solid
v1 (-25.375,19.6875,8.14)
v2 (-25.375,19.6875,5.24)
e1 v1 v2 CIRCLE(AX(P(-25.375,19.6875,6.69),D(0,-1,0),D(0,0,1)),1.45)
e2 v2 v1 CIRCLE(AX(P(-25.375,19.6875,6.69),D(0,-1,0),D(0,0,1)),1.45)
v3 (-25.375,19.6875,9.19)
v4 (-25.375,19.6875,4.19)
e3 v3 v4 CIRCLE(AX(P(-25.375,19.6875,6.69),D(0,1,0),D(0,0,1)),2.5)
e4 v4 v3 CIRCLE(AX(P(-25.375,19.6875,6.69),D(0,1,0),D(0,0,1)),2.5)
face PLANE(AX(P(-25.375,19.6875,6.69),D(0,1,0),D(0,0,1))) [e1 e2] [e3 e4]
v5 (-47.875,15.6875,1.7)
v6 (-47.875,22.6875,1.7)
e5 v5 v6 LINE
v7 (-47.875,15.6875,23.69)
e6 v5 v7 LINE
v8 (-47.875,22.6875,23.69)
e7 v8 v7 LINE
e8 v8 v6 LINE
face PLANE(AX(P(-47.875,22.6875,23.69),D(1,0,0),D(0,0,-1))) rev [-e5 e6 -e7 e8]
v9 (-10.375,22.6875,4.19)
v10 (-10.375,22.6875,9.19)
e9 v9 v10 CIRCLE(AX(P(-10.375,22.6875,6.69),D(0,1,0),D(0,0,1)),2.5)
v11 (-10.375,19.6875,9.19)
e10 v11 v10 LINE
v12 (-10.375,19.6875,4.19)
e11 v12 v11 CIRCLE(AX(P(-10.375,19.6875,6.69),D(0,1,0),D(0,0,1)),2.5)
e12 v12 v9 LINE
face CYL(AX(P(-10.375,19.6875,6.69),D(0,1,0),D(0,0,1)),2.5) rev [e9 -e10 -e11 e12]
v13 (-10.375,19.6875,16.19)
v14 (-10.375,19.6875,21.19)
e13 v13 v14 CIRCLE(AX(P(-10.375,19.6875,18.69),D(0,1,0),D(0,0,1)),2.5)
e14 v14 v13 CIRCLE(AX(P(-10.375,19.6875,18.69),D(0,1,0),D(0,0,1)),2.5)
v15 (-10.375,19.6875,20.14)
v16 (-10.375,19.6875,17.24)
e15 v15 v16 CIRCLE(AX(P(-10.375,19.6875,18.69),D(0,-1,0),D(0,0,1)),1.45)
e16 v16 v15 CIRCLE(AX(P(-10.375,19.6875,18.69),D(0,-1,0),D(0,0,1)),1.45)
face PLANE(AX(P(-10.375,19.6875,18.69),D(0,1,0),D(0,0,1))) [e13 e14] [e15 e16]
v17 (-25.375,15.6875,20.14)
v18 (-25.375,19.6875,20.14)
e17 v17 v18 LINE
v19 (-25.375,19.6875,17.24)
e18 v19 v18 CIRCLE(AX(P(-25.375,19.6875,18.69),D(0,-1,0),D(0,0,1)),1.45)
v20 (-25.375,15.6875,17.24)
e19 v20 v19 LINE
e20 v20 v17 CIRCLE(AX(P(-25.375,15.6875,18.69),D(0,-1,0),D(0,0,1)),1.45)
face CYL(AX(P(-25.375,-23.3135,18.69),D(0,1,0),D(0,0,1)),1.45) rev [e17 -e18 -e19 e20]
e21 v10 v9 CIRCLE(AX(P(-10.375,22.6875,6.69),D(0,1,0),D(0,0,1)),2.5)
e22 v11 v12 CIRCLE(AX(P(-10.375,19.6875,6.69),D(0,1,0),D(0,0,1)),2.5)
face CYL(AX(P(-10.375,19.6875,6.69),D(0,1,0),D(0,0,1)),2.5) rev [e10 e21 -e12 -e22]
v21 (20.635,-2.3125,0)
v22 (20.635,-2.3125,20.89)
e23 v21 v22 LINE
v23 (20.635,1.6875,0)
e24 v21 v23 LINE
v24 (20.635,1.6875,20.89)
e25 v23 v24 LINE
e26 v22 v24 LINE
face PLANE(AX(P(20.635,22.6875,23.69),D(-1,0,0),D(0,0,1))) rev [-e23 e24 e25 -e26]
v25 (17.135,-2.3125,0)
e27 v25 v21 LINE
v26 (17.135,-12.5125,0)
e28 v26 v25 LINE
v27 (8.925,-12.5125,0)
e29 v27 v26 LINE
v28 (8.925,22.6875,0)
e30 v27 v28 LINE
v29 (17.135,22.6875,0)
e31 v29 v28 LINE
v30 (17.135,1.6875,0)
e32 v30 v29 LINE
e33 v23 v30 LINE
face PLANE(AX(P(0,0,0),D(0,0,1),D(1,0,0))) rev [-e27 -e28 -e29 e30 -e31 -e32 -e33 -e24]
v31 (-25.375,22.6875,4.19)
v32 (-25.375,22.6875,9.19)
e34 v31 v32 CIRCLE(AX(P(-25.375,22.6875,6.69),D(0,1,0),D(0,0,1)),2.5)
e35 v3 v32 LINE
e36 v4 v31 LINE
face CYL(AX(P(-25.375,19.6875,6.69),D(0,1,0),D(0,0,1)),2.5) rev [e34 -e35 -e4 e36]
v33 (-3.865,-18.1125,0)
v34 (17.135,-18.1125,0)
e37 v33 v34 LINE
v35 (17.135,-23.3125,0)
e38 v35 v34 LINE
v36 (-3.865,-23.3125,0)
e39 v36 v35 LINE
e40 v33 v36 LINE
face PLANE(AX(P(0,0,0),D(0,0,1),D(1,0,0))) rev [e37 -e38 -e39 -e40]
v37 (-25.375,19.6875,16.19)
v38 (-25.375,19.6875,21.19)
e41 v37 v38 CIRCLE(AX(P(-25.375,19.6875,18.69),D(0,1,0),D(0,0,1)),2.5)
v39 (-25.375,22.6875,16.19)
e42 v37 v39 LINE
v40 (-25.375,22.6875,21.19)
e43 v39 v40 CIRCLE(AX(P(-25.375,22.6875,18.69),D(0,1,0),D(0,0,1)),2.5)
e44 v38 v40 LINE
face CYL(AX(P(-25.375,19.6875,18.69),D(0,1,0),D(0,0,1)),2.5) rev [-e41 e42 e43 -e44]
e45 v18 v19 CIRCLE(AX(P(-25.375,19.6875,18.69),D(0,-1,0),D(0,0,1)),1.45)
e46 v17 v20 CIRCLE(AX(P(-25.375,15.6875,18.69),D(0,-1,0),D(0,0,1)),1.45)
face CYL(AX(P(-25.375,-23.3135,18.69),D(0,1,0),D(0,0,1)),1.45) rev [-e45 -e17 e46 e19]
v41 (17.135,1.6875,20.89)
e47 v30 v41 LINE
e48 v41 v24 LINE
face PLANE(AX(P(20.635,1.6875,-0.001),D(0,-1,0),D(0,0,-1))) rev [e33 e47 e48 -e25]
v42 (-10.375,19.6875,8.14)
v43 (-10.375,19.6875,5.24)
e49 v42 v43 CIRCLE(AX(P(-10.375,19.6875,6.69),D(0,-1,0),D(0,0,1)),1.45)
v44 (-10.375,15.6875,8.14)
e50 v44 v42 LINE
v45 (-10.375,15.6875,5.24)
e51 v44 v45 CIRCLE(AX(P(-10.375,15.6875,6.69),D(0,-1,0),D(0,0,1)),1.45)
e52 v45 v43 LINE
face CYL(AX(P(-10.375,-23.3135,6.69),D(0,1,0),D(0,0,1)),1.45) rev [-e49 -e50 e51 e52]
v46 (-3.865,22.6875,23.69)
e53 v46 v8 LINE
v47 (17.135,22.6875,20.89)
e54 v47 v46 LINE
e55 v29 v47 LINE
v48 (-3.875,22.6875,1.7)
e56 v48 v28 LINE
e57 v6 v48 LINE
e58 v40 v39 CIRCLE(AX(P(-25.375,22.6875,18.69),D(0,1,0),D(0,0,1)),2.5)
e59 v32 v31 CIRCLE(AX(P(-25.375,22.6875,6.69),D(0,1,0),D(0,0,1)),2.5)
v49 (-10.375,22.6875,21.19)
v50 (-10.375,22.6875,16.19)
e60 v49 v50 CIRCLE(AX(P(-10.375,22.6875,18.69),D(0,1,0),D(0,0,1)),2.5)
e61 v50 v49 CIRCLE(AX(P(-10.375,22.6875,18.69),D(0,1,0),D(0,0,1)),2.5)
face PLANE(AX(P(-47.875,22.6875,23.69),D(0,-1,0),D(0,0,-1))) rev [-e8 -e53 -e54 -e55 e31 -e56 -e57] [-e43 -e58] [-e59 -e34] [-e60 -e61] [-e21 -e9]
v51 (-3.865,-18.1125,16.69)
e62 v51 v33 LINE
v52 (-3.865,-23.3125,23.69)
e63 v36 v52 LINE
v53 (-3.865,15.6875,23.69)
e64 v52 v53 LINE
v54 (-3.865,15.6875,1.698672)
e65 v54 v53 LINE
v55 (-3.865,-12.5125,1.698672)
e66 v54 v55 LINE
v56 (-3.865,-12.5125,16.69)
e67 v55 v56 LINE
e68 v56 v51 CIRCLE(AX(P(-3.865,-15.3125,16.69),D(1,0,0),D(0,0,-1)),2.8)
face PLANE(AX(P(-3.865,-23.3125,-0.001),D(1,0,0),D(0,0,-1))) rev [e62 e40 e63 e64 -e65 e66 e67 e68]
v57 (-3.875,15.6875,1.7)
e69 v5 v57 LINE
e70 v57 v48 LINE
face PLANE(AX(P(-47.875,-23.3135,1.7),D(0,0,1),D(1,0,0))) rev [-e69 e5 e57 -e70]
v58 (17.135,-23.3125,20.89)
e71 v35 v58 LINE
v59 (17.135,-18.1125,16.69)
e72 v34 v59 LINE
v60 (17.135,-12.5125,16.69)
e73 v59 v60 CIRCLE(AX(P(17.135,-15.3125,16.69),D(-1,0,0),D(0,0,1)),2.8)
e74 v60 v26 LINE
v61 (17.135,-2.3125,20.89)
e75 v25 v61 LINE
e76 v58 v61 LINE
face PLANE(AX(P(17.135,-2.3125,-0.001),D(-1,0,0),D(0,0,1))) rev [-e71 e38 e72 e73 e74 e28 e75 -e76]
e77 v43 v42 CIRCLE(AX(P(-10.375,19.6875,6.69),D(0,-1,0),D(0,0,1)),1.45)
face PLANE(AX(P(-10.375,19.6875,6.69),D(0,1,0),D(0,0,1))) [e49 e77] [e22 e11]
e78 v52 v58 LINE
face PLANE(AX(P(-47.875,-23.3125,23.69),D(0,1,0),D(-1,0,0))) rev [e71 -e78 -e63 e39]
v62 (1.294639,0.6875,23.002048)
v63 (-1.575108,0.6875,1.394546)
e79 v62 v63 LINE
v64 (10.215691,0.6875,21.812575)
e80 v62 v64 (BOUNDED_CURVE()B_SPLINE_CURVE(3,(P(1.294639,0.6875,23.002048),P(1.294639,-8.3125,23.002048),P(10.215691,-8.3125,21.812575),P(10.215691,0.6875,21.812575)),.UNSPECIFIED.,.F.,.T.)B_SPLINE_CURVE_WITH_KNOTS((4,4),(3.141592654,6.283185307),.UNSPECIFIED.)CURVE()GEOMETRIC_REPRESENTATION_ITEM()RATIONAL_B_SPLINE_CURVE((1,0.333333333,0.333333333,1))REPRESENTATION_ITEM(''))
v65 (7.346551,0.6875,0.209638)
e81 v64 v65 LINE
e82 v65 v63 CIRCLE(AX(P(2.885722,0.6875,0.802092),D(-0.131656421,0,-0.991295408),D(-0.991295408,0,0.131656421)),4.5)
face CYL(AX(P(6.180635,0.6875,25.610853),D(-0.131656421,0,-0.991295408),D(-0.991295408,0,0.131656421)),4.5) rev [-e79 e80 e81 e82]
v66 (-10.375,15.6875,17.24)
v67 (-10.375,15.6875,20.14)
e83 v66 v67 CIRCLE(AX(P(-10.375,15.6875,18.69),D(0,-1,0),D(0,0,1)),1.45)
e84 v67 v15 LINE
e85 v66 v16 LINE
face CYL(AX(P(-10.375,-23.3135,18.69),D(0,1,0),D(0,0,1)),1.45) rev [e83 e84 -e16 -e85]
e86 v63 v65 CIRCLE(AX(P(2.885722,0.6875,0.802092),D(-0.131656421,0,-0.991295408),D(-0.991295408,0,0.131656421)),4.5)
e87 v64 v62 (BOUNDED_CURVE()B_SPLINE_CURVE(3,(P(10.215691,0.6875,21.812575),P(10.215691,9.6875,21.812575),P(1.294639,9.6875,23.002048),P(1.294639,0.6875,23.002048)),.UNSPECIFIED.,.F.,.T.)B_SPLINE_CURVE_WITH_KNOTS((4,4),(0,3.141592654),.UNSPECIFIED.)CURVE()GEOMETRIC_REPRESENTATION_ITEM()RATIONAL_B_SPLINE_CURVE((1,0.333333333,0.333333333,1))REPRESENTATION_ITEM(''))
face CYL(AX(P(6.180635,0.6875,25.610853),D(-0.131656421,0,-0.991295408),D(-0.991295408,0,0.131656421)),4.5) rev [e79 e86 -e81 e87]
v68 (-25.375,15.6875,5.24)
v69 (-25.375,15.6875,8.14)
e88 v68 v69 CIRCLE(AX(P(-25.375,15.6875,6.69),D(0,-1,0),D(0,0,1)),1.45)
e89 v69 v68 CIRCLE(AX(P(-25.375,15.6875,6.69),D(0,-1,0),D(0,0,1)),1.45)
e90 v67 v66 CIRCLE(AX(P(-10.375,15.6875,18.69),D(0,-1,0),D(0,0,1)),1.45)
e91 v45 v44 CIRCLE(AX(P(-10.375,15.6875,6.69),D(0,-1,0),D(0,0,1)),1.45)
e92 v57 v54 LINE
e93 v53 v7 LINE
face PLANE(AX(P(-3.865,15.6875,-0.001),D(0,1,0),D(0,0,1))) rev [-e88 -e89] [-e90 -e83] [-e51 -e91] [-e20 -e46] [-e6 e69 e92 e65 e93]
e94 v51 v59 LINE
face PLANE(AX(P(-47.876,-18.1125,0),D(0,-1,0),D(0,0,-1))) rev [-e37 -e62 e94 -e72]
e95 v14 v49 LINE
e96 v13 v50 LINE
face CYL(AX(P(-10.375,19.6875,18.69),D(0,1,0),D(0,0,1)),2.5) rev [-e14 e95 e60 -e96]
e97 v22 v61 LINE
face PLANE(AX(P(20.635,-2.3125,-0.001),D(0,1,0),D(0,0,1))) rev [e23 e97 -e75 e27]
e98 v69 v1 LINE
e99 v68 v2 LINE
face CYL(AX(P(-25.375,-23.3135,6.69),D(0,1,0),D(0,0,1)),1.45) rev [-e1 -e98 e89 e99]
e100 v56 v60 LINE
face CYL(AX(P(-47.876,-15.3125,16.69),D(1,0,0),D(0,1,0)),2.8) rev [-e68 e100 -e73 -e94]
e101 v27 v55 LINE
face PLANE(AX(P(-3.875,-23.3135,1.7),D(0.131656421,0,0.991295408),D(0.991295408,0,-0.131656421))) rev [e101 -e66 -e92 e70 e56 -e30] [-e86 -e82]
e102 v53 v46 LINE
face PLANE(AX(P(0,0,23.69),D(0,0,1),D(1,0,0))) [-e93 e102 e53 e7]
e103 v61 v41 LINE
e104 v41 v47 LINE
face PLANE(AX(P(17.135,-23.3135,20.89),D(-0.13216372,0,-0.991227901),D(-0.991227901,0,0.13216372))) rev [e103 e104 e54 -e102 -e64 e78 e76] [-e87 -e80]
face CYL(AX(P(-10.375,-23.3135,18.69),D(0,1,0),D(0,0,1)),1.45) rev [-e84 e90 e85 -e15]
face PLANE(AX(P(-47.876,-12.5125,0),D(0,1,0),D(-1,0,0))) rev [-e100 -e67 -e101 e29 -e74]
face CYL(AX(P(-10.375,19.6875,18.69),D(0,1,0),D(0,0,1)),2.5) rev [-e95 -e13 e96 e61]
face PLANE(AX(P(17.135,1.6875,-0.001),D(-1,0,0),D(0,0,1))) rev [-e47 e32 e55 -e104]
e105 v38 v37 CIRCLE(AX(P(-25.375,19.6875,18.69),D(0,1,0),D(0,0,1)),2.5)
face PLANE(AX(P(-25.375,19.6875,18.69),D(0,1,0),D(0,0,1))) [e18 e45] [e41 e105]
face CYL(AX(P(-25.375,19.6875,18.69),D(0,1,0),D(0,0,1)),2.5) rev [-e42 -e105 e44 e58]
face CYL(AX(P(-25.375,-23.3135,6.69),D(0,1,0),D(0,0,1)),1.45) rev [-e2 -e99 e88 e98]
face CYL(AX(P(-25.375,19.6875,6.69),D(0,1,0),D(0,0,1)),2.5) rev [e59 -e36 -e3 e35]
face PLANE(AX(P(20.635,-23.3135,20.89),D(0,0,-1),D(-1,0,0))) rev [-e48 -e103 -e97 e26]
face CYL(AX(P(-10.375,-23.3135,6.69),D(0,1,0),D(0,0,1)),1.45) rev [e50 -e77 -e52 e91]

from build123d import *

# Parameters (mm, degrees)
SKETCH_1_W          = 68.51
SKETCH_1_H          = 46
EXTRUDE_1_DEPTH     = 23.69
CUT_EXTRUDE_1_REACH = 78.147
CUT_EXTRUDE_2_REACH = 72.493
CUT_EXTRUDE_3_REACH = 60.281
SKETCH_5_W          = 3.5
SKETCH_5_H          = 21
SKETCH_5_W_2        = 44.01
SKETCH_5_H_2        = 39
CUT_EXTRUDE_4_REACH = 59.946
SKETCH_6_R          = 4.5
CUT_EXTRUDE_5_REACH = 72.493
SKETCH_9_R          = 1.45
SKETCH_11_R         = 2.5
CUT_EXTRUDE_6_DEPTH = 3


with BuildPart() as part:
    # 草图1 → 凸台-拉伸1 (new body)
    with BuildSketch(Plane.XY):
        with Locations((-13.62, -0.3125)):
            Rectangle(SKETCH_1_W, SKETCH_1_H)
    extrude(amount=EXTRUDE_1_DEPTH)

    # 草图3 → 切除-拉伸1 (cut, up to next)
    with BuildSketch(Plane(origin=(20.635, 0, 0), x_dir=(0, 0, -1), z_dir=(1, 0, 0)), mode=Mode.PRIVATE) as cut_extrude_1_sk1:
        with BuildLine():
            Line((0, -18.1125), (-16.69, -18.1125))
            ThreePointArc((-16.69, -18.1125), (-19.49, -15.3125), (-16.69, -12.5125))
            Line((-16.69, -12.5125), (0, -12.5125))
            Line((0, -12.5125), (0, -18.1125))
        make_face()
    cut_extrude_1_tool1 = extrude(cut_extrude_1_sk1.sketch, amount=-CUT_EXTRUDE_1_REACH, mode=Mode.PRIVATE) & part.part
    add(cut_extrude_1_tool1.solids().sort_by_distance((20.635, -15.3125, 9.454896))[0], mode=Mode.SUBTRACT)

    # 草图4 → 切除-拉伸2 (cut, up to next)
    with BuildSketch(Plane(origin=(0, 22.6875, 0), x_dir=(1, 0, 0), z_dir=(0, 1, 0)), mode=Mode.PRIVATE) as cut_extrude_2_sk1:
        Polygon((20.635, -23.69), (20.635, -20.89), (17.135, -20.89), (-3.865, -23.69), align=None)
    cut_extrude_2_tool1 = extrude(cut_extrude_2_sk1.sketch, amount=-CUT_EXTRUDE_2_REACH, mode=Mode.PRIVATE) & part.part
    # 草图4 → 切除-拉伸2 (cut, up to next)
    with BuildSketch(Plane(origin=(0, 22.6875, 0), x_dir=(1, 0, 0), z_dir=(0, 1, 0)), mode=Mode.PRIVATE) as cut_extrude_2_sk2:
        Polygon((-47.875, 0), (-47.875, -1.7), (-3.875, -1.7), (8.925, 0), align=None)
    cut_extrude_2_tool2 = extrude(cut_extrude_2_sk2.sketch, amount=-CUT_EXTRUDE_2_REACH, mode=Mode.PRIVATE) & part.part
    add(cut_extrude_2_tool1.solids().sort_by_distance((12.3225, 22.6875, 22.64))[0], mode=Mode.SUBTRACT)
    add(cut_extrude_2_tool2.solids().sort_by_distance((-22.53955, 22.6875, 0.814021))[0], mode=Mode.SUBTRACT)

    # 草图5 → 切除-拉伸3 (cut, up to next)
    with BuildSketch(Plane.XY.offset(23.69), mode=Mode.PRIVATE) as cut_extrude_3_sk1:
        with Locations((18.885, -12.8125)):
            Rectangle(SKETCH_5_W, SKETCH_5_H)
    cut_extrude_3_tool1 = extrude(cut_extrude_3_sk1.sketch, amount=-CUT_EXTRUDE_3_REACH, mode=Mode.PRIVATE) & part.part
    # 草图5 → 切除-拉伸3 (cut, up to next)
    with BuildSketch(Plane.XY.offset(23.69), mode=Mode.PRIVATE) as cut_extrude_3_sk2:
        with Locations((18.885, 12.1875)):
            Rectangle(SKETCH_5_W, SKETCH_5_H)
    cut_extrude_3_tool2 = extrude(cut_extrude_3_sk2.sketch, amount=-CUT_EXTRUDE_3_REACH, mode=Mode.PRIVATE) & part.part
    # 草图5 → 切除-拉伸3 (cut, up to next)
    with BuildSketch(Plane.XY.offset(23.69), mode=Mode.PRIVATE) as cut_extrude_3_sk3:
        with Locations((-25.87, -3.8125)):
            Rectangle(SKETCH_5_W_2, SKETCH_5_H_2)
    cut_extrude_3_tool3 = extrude(cut_extrude_3_sk3.sketch, amount=-CUT_EXTRUDE_3_REACH, mode=Mode.PRIVATE) & part.part
    add(cut_extrude_3_tool1.solids().sort_by_distance((18.885, -12.8125, 23.69))[0], mode=Mode.SUBTRACT)
    add(cut_extrude_3_tool2.solids().sort_by_distance((18.885, 12.1875, 23.69))[0], mode=Mode.SUBTRACT)
    add(cut_extrude_3_tool3.solids().sort_by_distance((-25.87, -3.8125, 23.69))[0], mode=Mode.SUBTRACT)

    # 切除-拉伸4: up to this plane
    cut_extrude_4_end = Plane(origin=(17.135, -23.3135, 20.89), z_dir=(-0.13216372009101784, 0, -0.9912279006826348))
    # 草图6 → 切除-拉伸4 (cut, up to the surface)
    with BuildSketch(Plane(origin=(0.154700714, 0, 1.164805374), x_dir=(-0.9912954083909877, 0, 0.13165642142692813), z_dir=(-0.13165642142692813, 0, -0.9912954083909877)), mode=Mode.PRIVATE) as cut_extrude_4_sk1:
        with Locations((-2.755002186, 0.6875)):
            Circle(SKETCH_6_R)
    cut_extrude_4_tool1 = split(extrude(cut_extrude_4_sk1.sketch, amount=-CUT_EXTRUDE_4_REACH, mode=Mode.PRIVATE), bisect_by=cut_extrude_4_end, keep=Keep.BOTH, mode=Mode.PRIVATE)
    add(cut_extrude_4_tool1.solids().sort_by_distance((2.885722, 0.6875, 0.802092))[0], mode=Mode.SUBTRACT)

    # 草图9 → 切除-拉伸5 (cut, up to next)
    with BuildSketch(Plane(origin=(0, 22.6875, 0), x_dir=(1, 0, 0), z_dir=(0, 1, 0)), mode=Mode.PRIVATE) as cut_extrude_5_sk1:
        with Locations(Location((-25.375, -6.69, 0), (0, 0, 270))):
            Circle(SKETCH_9_R)
    cut_extrude_5_tool1 = extrude(cut_extrude_5_sk1.sketch, amount=-CUT_EXTRUDE_5_REACH, mode=Mode.PRIVATE) & part.part
    # 草图9 → 切除-拉伸5 (cut, up to next)
    with BuildSketch(Plane(origin=(0, 22.6875, 0), x_dir=(1, 0, 0), z_dir=(0, 1, 0)), mode=Mode.PRIVATE) as cut_extrude_5_sk2:
        with Locations(Location((-25.375, -18.69, 0), (0, 0, 270))):
            Circle(SKETCH_9_R)
    cut_extrude_5_tool2 = extrude(cut_extrude_5_sk2.sketch, amount=-CUT_EXTRUDE_5_REACH, mode=Mode.PRIVATE) & part.part
    # 草图9 → 切除-拉伸5 (cut, up to next)
    with BuildSketch(Plane(origin=(0, 22.6875, 0), x_dir=(1, 0, 0), z_dir=(0, 1, 0)), mode=Mode.PRIVATE) as cut_extrude_5_sk3:
        with Locations(Location((-10.375, -18.69, 0), (0, 0, 270))):
            Circle(SKETCH_9_R)
    cut_extrude_5_tool3 = extrude(cut_extrude_5_sk3.sketch, amount=-CUT_EXTRUDE_5_REACH, mode=Mode.PRIVATE) & part.part
    # 草图9 → 切除-拉伸5 (cut, up to next)
    with BuildSketch(Plane(origin=(0, 22.6875, 0), x_dir=(1, 0, 0), z_dir=(0, 1, 0)), mode=Mode.PRIVATE) as cut_extrude_5_sk4:
        with Locations(Location((-10.375, -6.69, 0), (0, 0, 270))):
            Circle(SKETCH_9_R)
    cut_extrude_5_tool4 = extrude(cut_extrude_5_sk4.sketch, amount=-CUT_EXTRUDE_5_REACH, mode=Mode.PRIVATE) & part.part
    add(cut_extrude_5_tool1.solids().sort_by_distance((-25.375, 22.6875, 6.69))[0], mode=Mode.SUBTRACT)
    add(cut_extrude_5_tool2.solids().sort_by_distance((-25.375, 22.6875, 18.69))[0], mode=Mode.SUBTRACT)
    add(cut_extrude_5_tool3.solids().sort_by_distance((-10.375, 22.6875, 18.69))[0], mode=Mode.SUBTRACT)
    add(cut_extrude_5_tool4.solids().sort_by_distance((-10.375, 22.6875, 6.69))[0], mode=Mode.SUBTRACT)

    # 草图11 → 切除-拉伸6 (cut)
    with BuildSketch(Plane(origin=(0, 22.6875, 0), x_dir=(1, 0, 0), z_dir=(0, 1, 0))):
        with Locations(Location((-25.375, -6.69, 0), (0, 0, 270))):
            Circle(SKETCH_11_R)
        with Locations(Location((-10.375, -6.69, 0), (0, 0, 270))):
            Circle(SKETCH_11_R)
        with Locations(Location((-25.375, -18.69, 0), (0, 0, 270))):
            Circle(SKETCH_11_R)
        with Locations(Location((-10.375, -18.69, 0), (0, 0, 270))):
            Circle(SKETCH_11_R)
    extrude(amount=-CUT_EXTRUDE_6_DEPTH, mode=Mode.SUBTRACT)


solid = part.part
